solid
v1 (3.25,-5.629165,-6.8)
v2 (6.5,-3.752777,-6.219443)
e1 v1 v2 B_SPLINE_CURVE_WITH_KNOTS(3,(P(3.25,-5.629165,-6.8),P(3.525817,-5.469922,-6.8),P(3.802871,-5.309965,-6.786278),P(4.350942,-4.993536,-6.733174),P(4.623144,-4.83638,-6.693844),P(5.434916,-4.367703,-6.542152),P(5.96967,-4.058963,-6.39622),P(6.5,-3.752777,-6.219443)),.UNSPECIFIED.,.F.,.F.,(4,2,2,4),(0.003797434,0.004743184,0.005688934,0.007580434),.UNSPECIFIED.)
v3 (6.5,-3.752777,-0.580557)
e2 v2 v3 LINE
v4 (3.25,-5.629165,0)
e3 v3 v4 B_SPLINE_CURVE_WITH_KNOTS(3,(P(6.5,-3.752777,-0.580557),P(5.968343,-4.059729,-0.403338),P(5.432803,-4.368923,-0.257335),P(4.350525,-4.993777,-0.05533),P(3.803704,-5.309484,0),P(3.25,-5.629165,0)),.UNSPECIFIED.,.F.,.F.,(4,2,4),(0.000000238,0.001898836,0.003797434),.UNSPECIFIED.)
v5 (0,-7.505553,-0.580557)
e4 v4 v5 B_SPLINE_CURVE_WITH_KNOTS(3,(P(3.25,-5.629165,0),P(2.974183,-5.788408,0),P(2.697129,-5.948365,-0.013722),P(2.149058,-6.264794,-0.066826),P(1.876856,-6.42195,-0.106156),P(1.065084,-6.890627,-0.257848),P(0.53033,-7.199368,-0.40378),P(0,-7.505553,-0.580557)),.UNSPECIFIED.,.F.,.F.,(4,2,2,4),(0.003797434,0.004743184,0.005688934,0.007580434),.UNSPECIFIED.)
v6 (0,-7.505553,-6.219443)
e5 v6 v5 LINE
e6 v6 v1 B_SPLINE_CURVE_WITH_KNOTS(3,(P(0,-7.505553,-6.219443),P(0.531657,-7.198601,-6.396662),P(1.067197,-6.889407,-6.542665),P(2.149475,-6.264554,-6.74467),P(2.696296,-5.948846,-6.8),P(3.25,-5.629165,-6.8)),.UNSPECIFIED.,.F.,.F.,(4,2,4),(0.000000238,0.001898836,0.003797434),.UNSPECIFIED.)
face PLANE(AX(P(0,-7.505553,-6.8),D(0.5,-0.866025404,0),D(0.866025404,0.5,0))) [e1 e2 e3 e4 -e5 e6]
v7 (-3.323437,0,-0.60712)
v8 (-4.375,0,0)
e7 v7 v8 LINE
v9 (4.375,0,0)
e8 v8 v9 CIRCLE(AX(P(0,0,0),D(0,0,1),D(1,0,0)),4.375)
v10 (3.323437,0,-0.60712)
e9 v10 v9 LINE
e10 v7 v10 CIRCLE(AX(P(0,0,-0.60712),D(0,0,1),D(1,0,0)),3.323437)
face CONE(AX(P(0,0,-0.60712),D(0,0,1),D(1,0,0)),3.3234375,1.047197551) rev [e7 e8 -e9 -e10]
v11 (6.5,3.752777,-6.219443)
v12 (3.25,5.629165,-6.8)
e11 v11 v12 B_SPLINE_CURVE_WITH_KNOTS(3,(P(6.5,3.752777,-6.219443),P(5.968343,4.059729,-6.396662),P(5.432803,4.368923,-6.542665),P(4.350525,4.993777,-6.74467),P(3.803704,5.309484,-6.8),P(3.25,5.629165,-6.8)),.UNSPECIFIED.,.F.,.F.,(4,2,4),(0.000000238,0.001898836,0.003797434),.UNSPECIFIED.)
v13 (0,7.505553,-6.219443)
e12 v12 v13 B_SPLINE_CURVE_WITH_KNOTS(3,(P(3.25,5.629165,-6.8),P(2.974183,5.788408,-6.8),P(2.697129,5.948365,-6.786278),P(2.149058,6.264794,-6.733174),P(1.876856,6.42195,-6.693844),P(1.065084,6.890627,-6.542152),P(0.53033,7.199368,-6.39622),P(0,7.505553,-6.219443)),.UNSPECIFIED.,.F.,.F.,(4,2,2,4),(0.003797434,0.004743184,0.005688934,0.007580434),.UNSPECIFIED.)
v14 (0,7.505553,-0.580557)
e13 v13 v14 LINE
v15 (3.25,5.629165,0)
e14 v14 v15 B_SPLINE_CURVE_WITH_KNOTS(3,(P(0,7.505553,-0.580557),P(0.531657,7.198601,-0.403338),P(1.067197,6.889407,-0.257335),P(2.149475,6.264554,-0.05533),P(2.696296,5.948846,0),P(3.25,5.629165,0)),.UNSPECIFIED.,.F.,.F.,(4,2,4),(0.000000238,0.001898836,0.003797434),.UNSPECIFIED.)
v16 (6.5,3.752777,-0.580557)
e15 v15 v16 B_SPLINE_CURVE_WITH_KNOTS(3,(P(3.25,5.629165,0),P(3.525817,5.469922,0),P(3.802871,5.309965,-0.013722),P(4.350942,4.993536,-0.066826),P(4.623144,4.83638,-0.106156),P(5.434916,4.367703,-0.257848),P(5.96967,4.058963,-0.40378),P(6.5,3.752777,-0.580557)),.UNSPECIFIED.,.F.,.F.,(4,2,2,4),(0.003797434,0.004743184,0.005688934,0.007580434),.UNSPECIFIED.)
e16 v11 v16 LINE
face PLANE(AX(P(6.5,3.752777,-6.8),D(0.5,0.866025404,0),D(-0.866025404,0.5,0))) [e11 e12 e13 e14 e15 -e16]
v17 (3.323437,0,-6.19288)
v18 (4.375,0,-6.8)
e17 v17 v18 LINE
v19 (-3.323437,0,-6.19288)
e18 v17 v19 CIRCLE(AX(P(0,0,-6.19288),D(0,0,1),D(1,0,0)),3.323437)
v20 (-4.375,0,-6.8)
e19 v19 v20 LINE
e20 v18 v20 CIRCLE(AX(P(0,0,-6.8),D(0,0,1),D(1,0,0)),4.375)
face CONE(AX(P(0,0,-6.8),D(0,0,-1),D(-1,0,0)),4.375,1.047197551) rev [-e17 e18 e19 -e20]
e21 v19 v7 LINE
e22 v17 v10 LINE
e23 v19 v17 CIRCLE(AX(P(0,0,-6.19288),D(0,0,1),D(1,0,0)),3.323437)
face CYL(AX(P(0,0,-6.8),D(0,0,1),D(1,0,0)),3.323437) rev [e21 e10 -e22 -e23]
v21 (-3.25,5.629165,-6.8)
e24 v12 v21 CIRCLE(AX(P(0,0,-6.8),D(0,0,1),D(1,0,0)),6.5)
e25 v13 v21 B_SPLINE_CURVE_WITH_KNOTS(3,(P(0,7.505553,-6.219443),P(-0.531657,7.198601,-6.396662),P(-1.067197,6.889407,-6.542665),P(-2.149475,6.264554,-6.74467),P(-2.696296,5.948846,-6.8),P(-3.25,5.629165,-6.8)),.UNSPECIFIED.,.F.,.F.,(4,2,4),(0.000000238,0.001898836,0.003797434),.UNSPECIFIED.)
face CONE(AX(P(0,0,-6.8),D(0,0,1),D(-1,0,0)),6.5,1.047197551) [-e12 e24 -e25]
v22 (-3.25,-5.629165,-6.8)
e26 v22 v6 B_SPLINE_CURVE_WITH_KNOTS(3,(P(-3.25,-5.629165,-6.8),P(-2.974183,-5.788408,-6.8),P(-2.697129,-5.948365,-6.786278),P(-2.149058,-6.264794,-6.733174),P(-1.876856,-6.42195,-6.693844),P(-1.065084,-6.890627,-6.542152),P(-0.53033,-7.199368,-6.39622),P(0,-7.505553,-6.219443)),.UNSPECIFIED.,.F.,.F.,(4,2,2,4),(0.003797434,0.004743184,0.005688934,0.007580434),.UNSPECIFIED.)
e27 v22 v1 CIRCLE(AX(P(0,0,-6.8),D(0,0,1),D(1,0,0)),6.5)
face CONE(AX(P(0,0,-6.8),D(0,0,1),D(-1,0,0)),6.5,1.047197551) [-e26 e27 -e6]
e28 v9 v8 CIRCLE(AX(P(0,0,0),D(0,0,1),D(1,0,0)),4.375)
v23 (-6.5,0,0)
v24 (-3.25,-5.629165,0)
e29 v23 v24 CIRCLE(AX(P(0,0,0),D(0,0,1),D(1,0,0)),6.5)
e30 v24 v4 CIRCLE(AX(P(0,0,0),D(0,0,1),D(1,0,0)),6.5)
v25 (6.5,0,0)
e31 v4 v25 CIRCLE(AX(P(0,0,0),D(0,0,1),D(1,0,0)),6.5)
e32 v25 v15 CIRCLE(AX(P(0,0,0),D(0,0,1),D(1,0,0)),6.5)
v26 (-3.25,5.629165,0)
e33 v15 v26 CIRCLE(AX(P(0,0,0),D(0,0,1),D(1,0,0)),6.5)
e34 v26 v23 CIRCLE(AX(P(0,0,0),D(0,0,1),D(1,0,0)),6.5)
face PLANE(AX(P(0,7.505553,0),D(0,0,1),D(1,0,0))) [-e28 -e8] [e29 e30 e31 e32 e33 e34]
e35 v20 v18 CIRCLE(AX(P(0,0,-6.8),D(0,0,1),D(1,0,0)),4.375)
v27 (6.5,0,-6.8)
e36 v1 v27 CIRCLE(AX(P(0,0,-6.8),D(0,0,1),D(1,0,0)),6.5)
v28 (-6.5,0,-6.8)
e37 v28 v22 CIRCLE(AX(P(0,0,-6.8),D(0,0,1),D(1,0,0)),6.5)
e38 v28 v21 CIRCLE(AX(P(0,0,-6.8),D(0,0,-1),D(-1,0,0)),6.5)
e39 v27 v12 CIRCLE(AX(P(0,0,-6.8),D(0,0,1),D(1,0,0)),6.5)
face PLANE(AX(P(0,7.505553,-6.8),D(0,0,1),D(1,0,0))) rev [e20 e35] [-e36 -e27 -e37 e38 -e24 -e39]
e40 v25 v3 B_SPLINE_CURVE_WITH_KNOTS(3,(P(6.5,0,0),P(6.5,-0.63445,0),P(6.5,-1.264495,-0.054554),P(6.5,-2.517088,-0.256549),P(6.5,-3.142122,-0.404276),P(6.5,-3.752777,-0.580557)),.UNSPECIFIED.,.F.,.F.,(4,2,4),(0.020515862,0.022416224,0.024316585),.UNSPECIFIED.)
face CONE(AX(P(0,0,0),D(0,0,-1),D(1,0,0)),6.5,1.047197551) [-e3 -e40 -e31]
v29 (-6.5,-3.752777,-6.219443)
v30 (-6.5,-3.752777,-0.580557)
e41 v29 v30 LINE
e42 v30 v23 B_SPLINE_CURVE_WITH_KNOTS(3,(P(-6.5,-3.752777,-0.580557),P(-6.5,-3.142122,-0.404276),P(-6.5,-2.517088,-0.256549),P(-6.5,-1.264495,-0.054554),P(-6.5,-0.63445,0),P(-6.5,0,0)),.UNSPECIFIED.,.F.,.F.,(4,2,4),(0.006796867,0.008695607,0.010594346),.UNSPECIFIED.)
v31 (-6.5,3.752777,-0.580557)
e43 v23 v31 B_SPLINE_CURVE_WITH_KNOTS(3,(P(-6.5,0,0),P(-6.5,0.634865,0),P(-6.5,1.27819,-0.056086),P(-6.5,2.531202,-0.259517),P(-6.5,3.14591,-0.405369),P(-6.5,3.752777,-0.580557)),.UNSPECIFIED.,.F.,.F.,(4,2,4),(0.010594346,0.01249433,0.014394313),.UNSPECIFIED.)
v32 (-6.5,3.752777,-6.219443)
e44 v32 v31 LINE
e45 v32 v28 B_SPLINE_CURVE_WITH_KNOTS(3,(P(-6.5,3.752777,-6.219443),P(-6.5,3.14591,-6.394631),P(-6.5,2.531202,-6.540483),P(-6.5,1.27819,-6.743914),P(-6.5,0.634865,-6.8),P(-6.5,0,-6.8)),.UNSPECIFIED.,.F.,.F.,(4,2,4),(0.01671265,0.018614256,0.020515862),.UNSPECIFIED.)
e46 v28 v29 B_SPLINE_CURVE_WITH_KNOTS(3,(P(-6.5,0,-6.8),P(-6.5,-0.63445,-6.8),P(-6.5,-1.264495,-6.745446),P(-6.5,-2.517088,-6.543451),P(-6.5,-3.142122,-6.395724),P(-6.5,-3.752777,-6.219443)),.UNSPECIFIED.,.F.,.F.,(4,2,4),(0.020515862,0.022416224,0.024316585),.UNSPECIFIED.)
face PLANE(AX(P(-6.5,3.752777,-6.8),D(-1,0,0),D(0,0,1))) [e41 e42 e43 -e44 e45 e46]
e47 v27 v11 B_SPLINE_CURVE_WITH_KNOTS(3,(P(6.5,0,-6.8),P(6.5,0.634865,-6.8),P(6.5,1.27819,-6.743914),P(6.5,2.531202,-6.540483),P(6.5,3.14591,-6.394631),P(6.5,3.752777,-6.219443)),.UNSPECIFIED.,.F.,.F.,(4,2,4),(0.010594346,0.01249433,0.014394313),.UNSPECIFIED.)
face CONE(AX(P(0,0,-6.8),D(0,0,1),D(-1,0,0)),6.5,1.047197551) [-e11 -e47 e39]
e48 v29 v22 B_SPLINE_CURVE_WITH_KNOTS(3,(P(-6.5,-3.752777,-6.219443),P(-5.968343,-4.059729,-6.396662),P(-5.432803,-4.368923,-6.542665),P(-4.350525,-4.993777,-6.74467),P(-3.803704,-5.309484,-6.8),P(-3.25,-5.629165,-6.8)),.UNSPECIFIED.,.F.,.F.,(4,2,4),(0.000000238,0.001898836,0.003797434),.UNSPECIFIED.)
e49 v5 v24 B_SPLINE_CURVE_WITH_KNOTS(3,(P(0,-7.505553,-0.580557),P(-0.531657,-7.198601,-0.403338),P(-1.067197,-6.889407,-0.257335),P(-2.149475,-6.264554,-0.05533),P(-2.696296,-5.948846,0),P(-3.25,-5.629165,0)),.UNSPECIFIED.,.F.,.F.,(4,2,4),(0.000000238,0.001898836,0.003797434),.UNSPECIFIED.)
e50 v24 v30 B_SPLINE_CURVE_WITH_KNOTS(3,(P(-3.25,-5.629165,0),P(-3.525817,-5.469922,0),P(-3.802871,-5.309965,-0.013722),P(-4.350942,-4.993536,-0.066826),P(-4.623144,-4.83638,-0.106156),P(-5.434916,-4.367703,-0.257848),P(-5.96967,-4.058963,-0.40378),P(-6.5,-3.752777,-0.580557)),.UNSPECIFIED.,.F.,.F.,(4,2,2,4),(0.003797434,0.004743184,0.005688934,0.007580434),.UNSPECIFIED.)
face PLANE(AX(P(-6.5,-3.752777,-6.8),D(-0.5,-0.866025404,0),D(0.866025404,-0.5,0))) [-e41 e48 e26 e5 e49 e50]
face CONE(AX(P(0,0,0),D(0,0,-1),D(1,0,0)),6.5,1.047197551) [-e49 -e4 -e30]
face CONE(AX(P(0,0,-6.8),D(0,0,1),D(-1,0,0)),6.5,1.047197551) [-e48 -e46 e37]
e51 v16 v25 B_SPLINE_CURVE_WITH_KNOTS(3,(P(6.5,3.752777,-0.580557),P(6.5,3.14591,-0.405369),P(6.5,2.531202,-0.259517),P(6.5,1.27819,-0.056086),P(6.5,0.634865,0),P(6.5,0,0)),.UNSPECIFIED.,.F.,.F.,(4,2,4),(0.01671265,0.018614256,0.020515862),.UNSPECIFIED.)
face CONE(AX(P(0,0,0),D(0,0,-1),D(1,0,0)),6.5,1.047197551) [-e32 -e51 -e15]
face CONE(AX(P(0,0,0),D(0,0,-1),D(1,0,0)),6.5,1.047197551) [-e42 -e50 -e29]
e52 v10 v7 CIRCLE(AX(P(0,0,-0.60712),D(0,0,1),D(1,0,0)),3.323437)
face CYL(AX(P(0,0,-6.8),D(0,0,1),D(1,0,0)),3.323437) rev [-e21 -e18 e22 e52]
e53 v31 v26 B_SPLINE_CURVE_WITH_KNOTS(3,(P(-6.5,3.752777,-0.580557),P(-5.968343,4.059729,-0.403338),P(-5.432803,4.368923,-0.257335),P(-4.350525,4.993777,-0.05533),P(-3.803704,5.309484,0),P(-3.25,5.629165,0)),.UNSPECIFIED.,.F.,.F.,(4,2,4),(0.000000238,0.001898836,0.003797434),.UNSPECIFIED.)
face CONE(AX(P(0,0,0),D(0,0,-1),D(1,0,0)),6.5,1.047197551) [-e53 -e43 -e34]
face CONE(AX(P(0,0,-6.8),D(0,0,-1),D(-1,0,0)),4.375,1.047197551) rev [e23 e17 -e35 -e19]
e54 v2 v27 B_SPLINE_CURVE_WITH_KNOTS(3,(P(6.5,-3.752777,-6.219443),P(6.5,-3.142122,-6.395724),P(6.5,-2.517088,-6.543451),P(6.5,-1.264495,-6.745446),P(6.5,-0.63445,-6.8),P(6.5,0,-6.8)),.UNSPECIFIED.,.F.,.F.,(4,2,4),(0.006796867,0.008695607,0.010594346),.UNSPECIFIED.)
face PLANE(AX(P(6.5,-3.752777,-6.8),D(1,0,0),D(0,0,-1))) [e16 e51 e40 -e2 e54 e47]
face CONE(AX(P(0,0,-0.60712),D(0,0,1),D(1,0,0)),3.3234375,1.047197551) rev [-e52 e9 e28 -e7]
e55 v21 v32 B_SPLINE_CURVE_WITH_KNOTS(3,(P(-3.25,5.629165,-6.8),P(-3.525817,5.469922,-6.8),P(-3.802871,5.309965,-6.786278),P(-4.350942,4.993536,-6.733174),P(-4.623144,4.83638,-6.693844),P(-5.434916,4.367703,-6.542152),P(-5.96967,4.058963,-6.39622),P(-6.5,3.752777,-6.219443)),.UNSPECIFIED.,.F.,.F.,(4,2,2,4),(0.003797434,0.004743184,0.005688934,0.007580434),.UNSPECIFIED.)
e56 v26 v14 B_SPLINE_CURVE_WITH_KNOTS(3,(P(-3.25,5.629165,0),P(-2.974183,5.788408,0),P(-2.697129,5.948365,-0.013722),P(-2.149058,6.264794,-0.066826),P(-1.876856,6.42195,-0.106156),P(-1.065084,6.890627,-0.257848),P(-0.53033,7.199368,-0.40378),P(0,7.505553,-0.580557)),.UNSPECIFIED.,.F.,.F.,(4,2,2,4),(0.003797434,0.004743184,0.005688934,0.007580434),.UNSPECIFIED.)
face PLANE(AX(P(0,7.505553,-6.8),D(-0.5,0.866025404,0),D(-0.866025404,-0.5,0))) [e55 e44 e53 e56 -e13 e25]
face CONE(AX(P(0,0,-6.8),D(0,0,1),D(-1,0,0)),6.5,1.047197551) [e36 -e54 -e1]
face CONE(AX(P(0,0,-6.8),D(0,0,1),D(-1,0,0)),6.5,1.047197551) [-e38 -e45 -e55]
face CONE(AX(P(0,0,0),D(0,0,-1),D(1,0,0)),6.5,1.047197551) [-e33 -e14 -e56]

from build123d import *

# Parameters (mm, degrees)
SKETCH_3_R          = 3.3234375
EXTRUDE_1_DEPTH     = 6.8
SKETCH_5_R          = 10.785
SKETCH_5_R_2        = 6.5
CUT_EXTRUDE_1_DEPTH = 1.36
CUT_EXTRUDE_1_DRAFT = -60
SKETCH_7_R          = 10.785
SKETCH_7_R_2        = 6.5
CUT_EXTRUDE_2_DEPTH = 1.36
CUT_EXTRUDE_2_DRAFT = -60


with BuildPart() as part:
    # 草图3 → 凸台-拉伸1 (new body)
    with BuildSketch(Plane.XY):
        Polygon((0, 7.505553499), (-6.5, 3.75277675), (-6.5, -3.75277675), (0, -7.505553499), (6.5, -3.75277675), (6.5, 3.75277675), align=None)
        Circle(SKETCH_3_R, mode=Mode.SUBTRACT)
    extrude(amount=-EXTRUDE_1_DEPTH)

    # 草图4 → 切除-旋转1 (revolve, cut)
    with BuildSketch(Plane(origin=(0, 0, 0), x_dir=(0, 0, -1), z_dir=(1, 0, 0)), mode=Mode.PRIVATE) as cut_revolve_1_sk:
        Polygon((0, 4.375), (0.607119892, 3.3234375), (0.607119892, 0), (0, 0), align=None)
        Polygon((6.8, 0), (6.8, 4.375), (6.192880108, 3.3234375), (6.192880108, 0), align=None)
    revolve(cut_revolve_1_sk.sketch.rotate(Axis((0, 0, 0), (0, 0, -1)), 90), axis=Axis((0, 0, 0), (0, 0, -1)), mode=Mode.SUBTRACT)


with BuildPart() as cut_extrude_1_tool:
    # 草图5 → 切除-拉伸1 (with draft: the straight prism first)
    with BuildSketch(Plane.XY):
        Circle(SKETCH_5_R)
        Circle(SKETCH_5_R_2, mode=Mode.SUBTRACT)
    extrude(amount=-CUT_EXTRUDE_1_DEPTH)
    # 切除-拉伸1: the draft: its side faces are tilted about the plane it starts from
    cut_extrude_1_sides = [cut_extrude_1_tool.faces().sort_by_distance(p)[0] for p in [
        (-10.785, 0, -0.68),
        (-6.5, 0, -0.68),
    ]]
    draft(cut_extrude_1_sides, Plane.XY, CUT_EXTRUDE_1_DRAFT)


with BuildPart() as part_1:
    add(part.part)

    # 切除-拉伸1: cut by cut_extrude_1_tool
    add(cut_extrude_1_tool.part, mode=Mode.SUBTRACT)


with BuildPart() as cut_extrude_2_tool:
    # 草图7 → 切除-拉伸2 (with draft: the straight prism first)
    with BuildSketch(Plane(origin=(0, 0, -6.8), x_dir=(-1, 0, 0), z_dir=(0, 0, -1))):
        Circle(SKETCH_7_R)
        Circle(SKETCH_7_R_2, mode=Mode.SUBTRACT)
    extrude(amount=-CUT_EXTRUDE_2_DEPTH)
    # 切除-拉伸2: the draft: its side faces are tilted about the plane it starts from
    cut_extrude_2_sides = [cut_extrude_2_tool.faces().sort_by_distance(p)[0] for p in [
        (10.785, 0, -6.12),
        (6.5, 0, -6.12),
    ]]
    draft(cut_extrude_2_sides, Plane(origin=(0, 0, -6.8), x_dir=(-1, 0, 0), z_dir=(0, 0, -1)), CUT_EXTRUDE_2_DRAFT)


with BuildPart() as part_2:
    add(part_1.part)

    # 切除-拉伸2: cut by cut_extrude_2_tool
    add(cut_extrude_2_tool.part, mode=Mode.SUBTRACT)


solid = part_2.part
